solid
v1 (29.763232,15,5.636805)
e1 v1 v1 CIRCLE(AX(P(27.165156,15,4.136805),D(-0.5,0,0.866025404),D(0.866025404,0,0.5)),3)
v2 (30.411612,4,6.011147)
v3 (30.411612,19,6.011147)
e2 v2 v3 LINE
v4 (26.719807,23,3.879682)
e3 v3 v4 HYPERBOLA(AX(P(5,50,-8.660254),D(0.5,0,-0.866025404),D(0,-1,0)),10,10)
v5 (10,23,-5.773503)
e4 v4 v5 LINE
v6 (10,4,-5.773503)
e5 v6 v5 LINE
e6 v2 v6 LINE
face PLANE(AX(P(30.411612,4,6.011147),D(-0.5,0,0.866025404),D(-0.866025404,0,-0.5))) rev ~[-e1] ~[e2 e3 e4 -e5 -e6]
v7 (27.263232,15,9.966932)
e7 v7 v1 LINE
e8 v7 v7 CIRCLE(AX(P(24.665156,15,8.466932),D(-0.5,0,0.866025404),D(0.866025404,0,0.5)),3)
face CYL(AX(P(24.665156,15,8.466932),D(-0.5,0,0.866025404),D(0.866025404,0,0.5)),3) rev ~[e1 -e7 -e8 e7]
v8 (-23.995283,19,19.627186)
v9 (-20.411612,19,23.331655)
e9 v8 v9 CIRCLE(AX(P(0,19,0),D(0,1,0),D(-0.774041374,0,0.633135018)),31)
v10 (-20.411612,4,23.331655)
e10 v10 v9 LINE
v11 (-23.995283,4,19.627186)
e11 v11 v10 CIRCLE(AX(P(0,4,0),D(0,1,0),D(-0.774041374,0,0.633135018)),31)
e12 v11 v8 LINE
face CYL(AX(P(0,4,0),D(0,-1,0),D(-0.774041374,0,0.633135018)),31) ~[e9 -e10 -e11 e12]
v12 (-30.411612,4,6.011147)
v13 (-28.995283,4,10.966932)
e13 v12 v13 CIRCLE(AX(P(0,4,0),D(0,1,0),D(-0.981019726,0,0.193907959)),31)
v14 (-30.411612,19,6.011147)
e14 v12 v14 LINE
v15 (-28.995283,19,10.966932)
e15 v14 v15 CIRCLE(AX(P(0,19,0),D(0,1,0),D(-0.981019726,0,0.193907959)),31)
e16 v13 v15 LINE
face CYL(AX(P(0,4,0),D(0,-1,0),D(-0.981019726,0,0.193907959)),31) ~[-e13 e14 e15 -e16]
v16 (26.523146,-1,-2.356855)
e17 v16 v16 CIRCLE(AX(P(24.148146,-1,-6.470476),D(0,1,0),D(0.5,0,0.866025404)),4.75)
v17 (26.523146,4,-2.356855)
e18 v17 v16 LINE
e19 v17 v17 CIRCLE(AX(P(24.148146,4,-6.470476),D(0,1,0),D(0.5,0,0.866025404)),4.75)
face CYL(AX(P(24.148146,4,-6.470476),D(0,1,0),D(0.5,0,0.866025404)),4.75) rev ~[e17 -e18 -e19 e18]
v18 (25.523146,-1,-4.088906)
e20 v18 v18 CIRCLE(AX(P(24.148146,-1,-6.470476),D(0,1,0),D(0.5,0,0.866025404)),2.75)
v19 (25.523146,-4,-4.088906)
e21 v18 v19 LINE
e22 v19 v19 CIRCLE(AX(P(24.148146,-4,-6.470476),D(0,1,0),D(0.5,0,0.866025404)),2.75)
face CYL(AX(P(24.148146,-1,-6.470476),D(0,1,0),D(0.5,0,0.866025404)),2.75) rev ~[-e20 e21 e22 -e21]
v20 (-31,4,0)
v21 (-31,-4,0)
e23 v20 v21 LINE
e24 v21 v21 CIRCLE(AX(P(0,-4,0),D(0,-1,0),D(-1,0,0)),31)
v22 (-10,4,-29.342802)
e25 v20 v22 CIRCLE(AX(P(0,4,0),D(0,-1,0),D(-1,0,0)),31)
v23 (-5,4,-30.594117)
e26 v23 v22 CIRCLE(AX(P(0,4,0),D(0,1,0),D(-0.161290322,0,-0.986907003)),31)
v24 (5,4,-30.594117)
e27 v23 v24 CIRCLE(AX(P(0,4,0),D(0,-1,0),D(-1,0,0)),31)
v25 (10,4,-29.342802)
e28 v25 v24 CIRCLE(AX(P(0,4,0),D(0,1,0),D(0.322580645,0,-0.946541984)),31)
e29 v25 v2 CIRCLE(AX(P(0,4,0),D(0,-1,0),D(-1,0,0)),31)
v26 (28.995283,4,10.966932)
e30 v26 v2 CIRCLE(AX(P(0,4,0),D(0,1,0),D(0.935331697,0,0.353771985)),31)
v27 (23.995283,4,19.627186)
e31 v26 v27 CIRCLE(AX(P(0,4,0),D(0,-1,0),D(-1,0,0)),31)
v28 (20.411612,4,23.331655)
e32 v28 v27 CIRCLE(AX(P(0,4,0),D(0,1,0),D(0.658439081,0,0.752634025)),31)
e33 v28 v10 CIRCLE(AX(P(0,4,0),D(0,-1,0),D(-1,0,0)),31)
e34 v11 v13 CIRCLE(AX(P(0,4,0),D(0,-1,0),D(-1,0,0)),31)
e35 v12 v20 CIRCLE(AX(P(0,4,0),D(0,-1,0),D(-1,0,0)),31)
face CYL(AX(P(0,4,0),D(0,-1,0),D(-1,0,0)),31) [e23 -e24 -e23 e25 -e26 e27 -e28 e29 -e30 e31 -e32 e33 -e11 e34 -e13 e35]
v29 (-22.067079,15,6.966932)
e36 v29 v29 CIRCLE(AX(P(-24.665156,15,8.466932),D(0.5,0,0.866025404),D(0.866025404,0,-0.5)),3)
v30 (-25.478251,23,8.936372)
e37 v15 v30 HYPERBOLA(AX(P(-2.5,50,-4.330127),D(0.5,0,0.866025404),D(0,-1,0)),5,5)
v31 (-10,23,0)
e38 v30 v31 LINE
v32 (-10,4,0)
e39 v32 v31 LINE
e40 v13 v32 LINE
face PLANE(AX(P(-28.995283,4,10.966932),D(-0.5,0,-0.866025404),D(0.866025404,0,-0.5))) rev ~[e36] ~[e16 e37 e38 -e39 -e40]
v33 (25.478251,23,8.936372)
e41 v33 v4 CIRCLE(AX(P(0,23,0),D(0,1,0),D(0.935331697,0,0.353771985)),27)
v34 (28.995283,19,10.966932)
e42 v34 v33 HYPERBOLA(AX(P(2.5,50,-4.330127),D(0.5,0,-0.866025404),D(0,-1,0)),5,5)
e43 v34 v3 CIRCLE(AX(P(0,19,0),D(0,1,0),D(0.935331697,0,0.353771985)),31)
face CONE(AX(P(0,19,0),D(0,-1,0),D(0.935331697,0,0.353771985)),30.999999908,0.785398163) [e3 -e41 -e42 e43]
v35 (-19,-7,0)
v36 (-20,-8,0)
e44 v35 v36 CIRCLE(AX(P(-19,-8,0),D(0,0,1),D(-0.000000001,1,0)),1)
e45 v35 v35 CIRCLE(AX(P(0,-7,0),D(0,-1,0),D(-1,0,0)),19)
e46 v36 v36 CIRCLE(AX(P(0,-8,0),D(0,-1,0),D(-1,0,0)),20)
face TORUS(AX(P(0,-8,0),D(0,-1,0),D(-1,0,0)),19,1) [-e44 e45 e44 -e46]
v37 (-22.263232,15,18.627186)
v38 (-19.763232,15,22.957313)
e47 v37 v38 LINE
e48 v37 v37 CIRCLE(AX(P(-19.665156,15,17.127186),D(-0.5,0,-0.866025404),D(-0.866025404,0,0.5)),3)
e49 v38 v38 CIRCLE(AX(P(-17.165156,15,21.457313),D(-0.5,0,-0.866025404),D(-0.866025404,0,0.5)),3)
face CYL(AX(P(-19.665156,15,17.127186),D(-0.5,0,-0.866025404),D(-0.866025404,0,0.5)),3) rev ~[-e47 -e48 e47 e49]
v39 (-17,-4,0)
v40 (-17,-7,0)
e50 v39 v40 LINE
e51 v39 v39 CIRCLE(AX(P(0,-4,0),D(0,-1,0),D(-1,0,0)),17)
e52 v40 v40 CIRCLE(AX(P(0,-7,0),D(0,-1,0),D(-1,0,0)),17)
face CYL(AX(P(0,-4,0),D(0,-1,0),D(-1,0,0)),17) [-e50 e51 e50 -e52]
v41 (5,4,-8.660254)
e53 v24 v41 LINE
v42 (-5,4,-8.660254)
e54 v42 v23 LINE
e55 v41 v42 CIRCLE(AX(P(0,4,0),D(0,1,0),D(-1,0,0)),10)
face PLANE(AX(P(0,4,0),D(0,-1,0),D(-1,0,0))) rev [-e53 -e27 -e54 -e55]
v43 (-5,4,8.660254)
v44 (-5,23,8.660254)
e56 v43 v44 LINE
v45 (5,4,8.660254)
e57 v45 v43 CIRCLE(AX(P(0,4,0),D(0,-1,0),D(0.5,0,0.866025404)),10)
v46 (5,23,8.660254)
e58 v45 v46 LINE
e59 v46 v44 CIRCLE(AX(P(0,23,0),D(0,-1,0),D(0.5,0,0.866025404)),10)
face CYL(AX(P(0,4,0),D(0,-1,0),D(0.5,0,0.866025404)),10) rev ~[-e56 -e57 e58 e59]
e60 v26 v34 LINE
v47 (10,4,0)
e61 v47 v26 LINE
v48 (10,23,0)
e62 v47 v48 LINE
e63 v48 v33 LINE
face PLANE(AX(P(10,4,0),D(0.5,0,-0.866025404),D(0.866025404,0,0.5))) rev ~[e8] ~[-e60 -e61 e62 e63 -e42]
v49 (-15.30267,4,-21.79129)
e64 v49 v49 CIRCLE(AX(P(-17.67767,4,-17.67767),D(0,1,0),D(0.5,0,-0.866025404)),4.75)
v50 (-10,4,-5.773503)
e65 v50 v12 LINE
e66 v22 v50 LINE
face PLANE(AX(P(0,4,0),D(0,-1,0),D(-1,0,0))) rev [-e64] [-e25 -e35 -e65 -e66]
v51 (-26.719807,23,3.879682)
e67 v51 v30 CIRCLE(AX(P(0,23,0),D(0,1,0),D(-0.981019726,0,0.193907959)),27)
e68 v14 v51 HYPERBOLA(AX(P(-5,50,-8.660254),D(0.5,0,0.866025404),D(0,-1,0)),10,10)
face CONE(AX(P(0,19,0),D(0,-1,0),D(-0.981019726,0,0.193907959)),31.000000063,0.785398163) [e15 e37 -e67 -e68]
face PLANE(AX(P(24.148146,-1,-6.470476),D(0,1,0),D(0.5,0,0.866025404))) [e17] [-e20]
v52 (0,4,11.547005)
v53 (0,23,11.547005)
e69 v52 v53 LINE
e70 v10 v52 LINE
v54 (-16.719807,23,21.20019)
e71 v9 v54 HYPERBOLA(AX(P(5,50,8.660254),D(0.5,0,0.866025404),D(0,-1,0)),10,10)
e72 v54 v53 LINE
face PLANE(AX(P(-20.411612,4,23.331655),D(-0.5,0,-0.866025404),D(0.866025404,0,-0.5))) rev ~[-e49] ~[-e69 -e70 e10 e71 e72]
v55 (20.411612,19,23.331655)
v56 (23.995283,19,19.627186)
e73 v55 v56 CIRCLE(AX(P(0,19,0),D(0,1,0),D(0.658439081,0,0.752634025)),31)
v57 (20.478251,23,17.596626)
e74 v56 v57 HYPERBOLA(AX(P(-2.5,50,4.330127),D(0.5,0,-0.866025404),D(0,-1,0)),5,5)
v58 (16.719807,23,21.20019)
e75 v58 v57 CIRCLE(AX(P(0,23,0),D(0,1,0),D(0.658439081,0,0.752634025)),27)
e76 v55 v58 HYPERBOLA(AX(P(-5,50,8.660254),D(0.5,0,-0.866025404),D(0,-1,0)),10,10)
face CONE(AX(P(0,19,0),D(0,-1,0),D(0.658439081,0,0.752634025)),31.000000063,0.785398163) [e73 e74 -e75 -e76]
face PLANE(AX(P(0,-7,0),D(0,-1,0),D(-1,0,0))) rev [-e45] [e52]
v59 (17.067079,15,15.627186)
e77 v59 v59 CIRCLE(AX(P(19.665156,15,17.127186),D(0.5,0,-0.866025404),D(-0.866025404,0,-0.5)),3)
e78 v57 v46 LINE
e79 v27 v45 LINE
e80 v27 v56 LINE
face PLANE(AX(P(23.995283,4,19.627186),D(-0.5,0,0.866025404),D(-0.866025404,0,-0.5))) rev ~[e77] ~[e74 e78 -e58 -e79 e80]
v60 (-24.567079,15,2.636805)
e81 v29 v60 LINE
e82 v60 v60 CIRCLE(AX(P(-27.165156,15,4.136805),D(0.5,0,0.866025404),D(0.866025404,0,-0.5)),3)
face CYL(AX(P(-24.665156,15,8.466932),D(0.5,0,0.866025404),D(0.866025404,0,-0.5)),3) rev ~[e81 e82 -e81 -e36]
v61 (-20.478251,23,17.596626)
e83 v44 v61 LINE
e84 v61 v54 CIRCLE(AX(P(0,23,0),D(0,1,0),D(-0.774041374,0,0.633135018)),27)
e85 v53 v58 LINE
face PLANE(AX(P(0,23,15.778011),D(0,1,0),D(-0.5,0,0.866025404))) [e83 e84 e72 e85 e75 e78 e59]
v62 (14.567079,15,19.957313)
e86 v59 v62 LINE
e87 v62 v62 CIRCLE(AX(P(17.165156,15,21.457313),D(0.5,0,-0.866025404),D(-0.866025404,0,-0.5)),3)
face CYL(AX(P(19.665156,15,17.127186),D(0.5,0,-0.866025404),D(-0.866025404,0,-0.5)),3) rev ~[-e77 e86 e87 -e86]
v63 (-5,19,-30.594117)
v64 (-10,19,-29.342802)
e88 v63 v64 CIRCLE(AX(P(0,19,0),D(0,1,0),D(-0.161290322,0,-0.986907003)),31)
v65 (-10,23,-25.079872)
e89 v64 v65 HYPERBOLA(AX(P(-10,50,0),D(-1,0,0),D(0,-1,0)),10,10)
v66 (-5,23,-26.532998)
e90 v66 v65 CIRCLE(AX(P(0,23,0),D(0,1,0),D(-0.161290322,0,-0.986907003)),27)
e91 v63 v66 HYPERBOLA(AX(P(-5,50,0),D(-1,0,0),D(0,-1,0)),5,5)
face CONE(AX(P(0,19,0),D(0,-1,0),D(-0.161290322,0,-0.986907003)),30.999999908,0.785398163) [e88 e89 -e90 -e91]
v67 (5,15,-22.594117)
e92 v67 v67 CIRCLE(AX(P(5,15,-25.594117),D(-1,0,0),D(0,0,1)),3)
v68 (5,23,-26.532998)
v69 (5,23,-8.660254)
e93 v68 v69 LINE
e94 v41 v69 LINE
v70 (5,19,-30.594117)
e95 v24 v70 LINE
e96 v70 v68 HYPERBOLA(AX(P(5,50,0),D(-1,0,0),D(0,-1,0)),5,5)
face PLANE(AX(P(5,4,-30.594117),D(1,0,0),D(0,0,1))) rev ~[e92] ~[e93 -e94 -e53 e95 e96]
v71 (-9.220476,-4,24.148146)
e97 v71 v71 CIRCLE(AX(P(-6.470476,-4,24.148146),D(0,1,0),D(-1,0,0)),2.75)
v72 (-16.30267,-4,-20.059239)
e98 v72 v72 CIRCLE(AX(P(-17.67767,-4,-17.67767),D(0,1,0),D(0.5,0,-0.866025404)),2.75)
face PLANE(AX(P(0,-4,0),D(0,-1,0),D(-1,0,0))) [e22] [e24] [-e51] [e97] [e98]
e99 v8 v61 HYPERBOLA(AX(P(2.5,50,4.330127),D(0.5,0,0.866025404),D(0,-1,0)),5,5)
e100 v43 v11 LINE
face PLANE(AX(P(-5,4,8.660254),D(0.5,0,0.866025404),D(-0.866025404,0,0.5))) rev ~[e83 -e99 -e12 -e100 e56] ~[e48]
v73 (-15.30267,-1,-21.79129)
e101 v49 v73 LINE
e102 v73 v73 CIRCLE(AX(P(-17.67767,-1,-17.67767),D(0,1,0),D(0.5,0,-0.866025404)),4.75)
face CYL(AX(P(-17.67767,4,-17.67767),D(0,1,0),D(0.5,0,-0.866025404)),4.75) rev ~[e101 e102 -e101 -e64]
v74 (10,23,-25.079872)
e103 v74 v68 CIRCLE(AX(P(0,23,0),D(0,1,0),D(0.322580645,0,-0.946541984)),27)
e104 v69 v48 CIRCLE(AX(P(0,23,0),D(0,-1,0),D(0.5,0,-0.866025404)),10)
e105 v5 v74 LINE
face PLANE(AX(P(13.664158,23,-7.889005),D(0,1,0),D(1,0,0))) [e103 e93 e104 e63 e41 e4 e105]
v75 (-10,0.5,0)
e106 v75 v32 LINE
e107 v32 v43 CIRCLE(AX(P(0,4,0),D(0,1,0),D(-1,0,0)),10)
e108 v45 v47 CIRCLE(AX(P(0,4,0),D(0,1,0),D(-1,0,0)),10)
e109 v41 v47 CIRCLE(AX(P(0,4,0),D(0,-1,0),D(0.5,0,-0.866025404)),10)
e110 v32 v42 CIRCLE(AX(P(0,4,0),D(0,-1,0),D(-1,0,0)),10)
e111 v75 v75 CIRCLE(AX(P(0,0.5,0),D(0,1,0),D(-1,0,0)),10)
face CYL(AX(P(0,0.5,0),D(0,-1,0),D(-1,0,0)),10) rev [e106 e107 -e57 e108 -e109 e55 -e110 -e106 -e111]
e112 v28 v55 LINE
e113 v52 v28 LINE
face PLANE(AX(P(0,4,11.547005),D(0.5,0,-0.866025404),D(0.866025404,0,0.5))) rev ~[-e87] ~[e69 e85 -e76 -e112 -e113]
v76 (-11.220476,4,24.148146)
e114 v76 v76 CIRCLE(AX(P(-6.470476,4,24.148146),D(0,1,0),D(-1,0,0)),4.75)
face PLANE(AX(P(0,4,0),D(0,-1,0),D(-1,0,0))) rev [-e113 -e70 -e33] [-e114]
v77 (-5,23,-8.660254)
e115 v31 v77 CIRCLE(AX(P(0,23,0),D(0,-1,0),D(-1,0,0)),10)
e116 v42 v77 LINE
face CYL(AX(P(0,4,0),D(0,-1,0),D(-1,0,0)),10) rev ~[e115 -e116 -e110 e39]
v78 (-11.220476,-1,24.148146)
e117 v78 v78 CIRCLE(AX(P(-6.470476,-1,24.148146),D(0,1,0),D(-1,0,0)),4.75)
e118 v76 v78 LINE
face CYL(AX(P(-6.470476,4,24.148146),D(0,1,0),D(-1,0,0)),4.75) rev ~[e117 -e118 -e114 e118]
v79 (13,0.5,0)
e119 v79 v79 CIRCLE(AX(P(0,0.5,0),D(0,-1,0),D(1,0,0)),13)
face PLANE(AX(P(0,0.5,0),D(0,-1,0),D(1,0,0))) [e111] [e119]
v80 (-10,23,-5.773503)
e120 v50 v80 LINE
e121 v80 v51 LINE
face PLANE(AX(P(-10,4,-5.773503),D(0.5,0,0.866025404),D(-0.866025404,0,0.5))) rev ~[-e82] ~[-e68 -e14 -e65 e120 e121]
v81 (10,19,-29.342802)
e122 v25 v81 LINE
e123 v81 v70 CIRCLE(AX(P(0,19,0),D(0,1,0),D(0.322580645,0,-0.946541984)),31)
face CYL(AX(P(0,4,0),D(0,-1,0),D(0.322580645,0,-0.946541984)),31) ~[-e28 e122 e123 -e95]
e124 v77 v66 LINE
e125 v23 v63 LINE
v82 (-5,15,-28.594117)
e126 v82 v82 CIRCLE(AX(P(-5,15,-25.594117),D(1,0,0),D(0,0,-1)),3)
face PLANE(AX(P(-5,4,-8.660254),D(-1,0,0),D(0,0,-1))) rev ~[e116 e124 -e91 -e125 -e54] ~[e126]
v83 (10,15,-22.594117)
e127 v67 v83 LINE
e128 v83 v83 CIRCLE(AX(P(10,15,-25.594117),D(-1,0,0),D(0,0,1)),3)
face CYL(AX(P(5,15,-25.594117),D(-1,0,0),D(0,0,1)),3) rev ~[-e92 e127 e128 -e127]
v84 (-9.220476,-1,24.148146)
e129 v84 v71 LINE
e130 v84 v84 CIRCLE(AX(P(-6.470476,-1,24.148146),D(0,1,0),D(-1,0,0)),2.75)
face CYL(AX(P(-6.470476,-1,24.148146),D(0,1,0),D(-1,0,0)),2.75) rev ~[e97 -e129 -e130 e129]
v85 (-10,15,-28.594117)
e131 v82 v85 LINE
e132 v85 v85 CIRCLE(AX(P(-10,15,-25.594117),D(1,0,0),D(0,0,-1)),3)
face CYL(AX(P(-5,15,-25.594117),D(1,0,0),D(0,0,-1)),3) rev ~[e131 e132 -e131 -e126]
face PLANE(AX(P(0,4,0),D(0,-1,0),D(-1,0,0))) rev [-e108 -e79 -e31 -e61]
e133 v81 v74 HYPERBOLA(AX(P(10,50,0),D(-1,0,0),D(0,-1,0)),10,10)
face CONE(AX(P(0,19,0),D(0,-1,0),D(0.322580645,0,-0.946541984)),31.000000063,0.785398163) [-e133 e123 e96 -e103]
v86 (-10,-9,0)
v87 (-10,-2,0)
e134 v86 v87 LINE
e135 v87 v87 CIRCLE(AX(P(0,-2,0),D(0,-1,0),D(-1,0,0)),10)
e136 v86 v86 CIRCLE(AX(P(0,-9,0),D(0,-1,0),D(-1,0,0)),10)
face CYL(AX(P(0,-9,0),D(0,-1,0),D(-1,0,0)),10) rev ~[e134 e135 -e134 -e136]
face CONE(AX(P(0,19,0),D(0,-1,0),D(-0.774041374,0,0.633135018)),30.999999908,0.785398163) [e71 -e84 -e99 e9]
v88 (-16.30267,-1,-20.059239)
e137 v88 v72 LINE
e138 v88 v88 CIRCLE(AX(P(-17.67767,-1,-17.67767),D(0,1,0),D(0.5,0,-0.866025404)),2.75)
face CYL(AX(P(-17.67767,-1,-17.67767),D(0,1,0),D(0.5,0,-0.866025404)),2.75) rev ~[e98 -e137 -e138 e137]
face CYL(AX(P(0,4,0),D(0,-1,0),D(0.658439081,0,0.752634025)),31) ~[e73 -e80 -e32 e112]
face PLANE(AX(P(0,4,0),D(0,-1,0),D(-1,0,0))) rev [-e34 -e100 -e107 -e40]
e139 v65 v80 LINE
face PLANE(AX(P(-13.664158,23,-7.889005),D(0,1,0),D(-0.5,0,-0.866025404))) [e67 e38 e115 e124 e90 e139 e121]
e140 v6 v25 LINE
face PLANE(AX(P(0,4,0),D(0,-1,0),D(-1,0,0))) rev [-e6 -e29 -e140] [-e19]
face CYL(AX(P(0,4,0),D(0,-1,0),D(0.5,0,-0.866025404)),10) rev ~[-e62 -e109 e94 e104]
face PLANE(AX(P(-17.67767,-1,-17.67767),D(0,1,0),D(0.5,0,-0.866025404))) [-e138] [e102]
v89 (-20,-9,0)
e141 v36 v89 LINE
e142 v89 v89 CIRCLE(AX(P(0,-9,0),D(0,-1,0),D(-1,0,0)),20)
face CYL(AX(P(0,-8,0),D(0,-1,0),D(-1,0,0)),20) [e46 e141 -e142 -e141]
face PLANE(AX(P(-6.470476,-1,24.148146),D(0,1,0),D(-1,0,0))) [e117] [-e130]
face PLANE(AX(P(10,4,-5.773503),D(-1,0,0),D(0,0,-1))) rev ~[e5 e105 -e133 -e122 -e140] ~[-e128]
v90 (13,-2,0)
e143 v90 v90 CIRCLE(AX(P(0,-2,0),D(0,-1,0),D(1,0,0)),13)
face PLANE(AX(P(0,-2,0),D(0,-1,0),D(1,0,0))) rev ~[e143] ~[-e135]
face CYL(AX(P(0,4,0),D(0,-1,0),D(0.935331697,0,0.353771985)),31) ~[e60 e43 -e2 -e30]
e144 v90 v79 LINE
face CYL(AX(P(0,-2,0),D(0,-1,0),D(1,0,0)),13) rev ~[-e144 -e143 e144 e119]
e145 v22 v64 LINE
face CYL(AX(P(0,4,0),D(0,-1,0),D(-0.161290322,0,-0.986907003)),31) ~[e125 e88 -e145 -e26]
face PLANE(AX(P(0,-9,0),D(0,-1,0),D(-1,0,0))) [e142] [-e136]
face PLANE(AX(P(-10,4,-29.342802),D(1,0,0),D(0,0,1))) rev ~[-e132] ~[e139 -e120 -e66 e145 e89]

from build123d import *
from build123d.topology import SkipClean

# Parameters (mm, degrees)
LUG_DEPTH                         = 19
LUG_PIN_HOLE_A_SKETCH_R           = 3
LUG_PIN_HOLE_A_6_DEPTH            = 19
LUG_PIN_HOLE_B_SKETCH_R           = 3
LUG_PIN_HOLE_B_6_DEPTH            = 19
LUG_PATTERN_3X120_COUNT           = 3
LUG_CHAMFER_4MM_SIZE              = 4
BORE_START                        = -3.5
BORE_RECESS_SKETCH_R              = 10
BORE_RECESS_20_X3_5_DEPTH         = 3.5
CENTRE_BORE_SKETCH_R              = 10
CENTRE_BORE_20_X7_DEPTH           = 7
COUNTERBORE_SKETCH_R              = 13
COUNTERBORE_26_X2_5_DEPTH         = 2.5
RADIAL_SLOT_PROFILE_R             = 4.75
RADIAL_SLOT_DEPTH                 = 5
FLANGE_HOLE_SKETCH_R              = 2.75
FLANGE_HOLE_5_5_DEPTH             = 50.979995998
SLOT_AND_HOLE_PATTERN_3X120_COUNT = 3


with BuildPart() as part:
    # Base Flange Profile → Base Flange Ø62 (revolve)
    with BuildSketch(Plane.XY):
        with BuildLine():
            Line((-31, 4), (-31, -4))
            Line((-31, -4), (-17, -4))
            Line((-17, -4), (-17, -7))
            Line((-17, -7), (-19, -7))
            ThreePointArc((-19, -7), (-19.707106781, -7.292893219), (-20, -8))
            Line((-20, -8), (-20, -9))
            Line((-20, -9), (0, -9))
            Line((0, -9), (0, 4))
            Line((0, 4), (-31, 4))
        make_face()
    revolve(axis=Axis((0, 39.539668131, 0), (0, -1, 0)))

    # Lug Profile → Lug (add)
    with SkipClean():  # the faces are left unmerged after this step: merging them gives an invalid solid
        with BuildSketch(Plane(origin=(0, 4, 0), x_dir=(1, 0, 0), z_dir=(0, 1, 0))):
            with BuildLine():
                Line((5, 30.594117082), (5, 8.660254038))
                ThreePointArc((5, 8.660254038), (8.660254038, 5), (10, 0))
                Line((10, 0), (28.995282599, -10.966931522))
                ThreePointArc((28.995282599, -10.966931522), (29.806622049, -8.518525814), (30.411611519, -6.011146713))
                Line((30.411611519, -6.011146713), (10, 5.773502692))
                Line((10, 5.773502692), (10, 29.342801502))
                ThreePointArc((10, 29.342801502), (7.526051267, 30.072554802), (5, 30.594117082))
            make_face()
        lug = extrude(amount=LUG_DEPTH)

    # Lug Pin Hole A Sketch → Lug Pin Hole A Ø6 (cut)
    with SkipClean():  # the faces are left unmerged after this step: merging them gives an invalid solid
        with BuildSketch(Plane.ZY.offset(-5)):
            with Locations((-25.594117082, 15)):
                Circle(LUG_PIN_HOLE_A_SKETCH_R)
        lug_pin_hole_a_6 = extrude(amount=-LUG_PIN_HOLE_A_6_DEPTH, mode=Mode.SUBTRACT)

    # Lug Pin Hole B Sketch → Lug Pin Hole B Ø6 (cut)
    with SkipClean():  # the faces are left unmerged after this step: merging them gives an invalid solid
        with BuildSketch(Plane(origin=(2.5, 0, -4.330127019), x_dir=(0.8660254037844399, 0, 0.4999999999999978), z_dir=(-0.4999999999999978, 0, 0.8660254037844399))):
            with Locations((25.594117082, 15)):
                Circle(LUG_PIN_HOLE_B_SKETCH_R)
        lug_pin_hole_b_6 = extrude(amount=-LUG_PIN_HOLE_B_6_DEPTH, mode=Mode.SUBTRACT)

    # Lug Pattern 3x120°: Lug, Lug Pin Hole A Ø6, Lug Pin Hole B Ø6 ×3 about axis
    with SkipClean():  # the faces are left unmerged after this step: merging them gives an invalid solid
        lug_pattern_3x120_axis = Axis((0, 0, 0), (0, 1, 0))
        add([lug.rotate(lug_pattern_3x120_axis, i * 360 / LUG_PATTERN_3X120_COUNT) for i in range(1, LUG_PATTERN_3X120_COUNT)])
        add([lug_pin_hole_a_6.rotate(lug_pattern_3x120_axis, i * 360 / LUG_PATTERN_3X120_COUNT) for i in range(1, LUG_PATTERN_3X120_COUNT)], mode=Mode.SUBTRACT)
        add([lug_pin_hole_b_6.rotate(lug_pattern_3x120_axis, i * 360 / LUG_PATTERN_3X120_COUNT) for i in range(1, LUG_PATTERN_3X120_COUNT)], mode=Mode.SUBTRACT)

    # Lug Chamfer 4mm
    lug_chamfer_4mm_edges = [part.edges().sort_by_distance(p)[0] for p in [
        (29.806622049, 23, 8.518525814),
        (7.526051267, 23, -30.072554802),
        (-7.526051267, 23, -30.072554802),
        (-29.806622049, 23, 8.518525814),
        (-22.280570782, 23, 21.554028988),
        (22.280570782, 23, 21.554028988),
    ]]
    chamfer(lug_chamfer_4mm_edges, length=LUG_CHAMFER_4MM_SIZE)

    # Bore Recess Sketch → Bore Recess Ø20 x3.5 (cut)
    with BuildSketch(Plane(origin=(0, 4, 0), x_dir=(1, 0, 0), z_dir=(0, 1, 0)).offset(BORE_START)):
        with Locations(Location((0, 0, 0), (0, 0, 180))):
            Circle(BORE_RECESS_SKETCH_R)
    extrude(amount=BORE_RECESS_20_X3_5_DEPTH, mode=Mode.SUBTRACT)

    # Centre Bore Sketch → Centre Bore Ø20 x7 (cut)
    with BuildSketch(Plane.XZ.offset(9)):
        with Locations(Location((0, 0, 0), (0, 0, 180))):
            Circle(CENTRE_BORE_SKETCH_R)
    extrude(amount=-CENTRE_BORE_20_X7_DEPTH, mode=Mode.SUBTRACT)

    # Counterbore Sketch → Counterbore Ø26 x2.5 (cut)
    with BuildSketch(Plane.XZ.offset(2)):
        Circle(COUNTERBORE_SKETCH_R)
    extrude(amount=-COUNTERBORE_26_X2_5_DEPTH, mode=Mode.SUBTRACT)

    # Radial Slot Profile → Radial Slot (cut)
    with BuildSketch(Plane(origin=(0, 4, 0), x_dir=(1, 0, 0), z_dir=(0, 1, 0))):
        with Locations(Location((-6.470476128, -24.148145657, 0), (0, 0, 180))):
            Circle(RADIAL_SLOT_PROFILE_R)
    radial_slot = extrude(amount=-RADIAL_SLOT_DEPTH, mode=Mode.SUBTRACT)

    # Flange Hole Sketch → Flange Hole Ø5.5 (cut, through all)
    with BuildSketch(Plane(origin=(0, -1, 0), x_dir=(1, 0, 0), z_dir=(0, 1, 0))):
        with Locations(Location((-6.470476128, -24.148145657, 0), (0, 0, 180))):
            Circle(FLANGE_HOLE_SKETCH_R)
    flange_hole_5_5 = extrude(amount=-FLANGE_HOLE_5_5_DEPTH, mode=Mode.SUBTRACT)

    # Slot and Hole Pattern 3x120°: Radial Slot, Flange Hole Ø5.5 ×3 about axis
    slot_and_hole_pattern_3x120_axis = Axis((0, 0, 0), (0, 1, 0))
    add([radial_slot.rotate(slot_and_hole_pattern_3x120_axis, i * 360 / SLOT_AND_HOLE_PATTERN_3X120_COUNT) for i in range(1, SLOT_AND_HOLE_PATTERN_3X120_COUNT)], mode=Mode.SUBTRACT)
    add([flange_hole_5_5.rotate(slot_and_hole_pattern_3x120_axis, i * 360 / SLOT_AND_HOLE_PATTERN_3X120_COUNT) for i in range(1, SLOT_AND_HOLE_PATTERN_3X120_COUNT)], mode=Mode.SUBTRACT)


solid = part.part
